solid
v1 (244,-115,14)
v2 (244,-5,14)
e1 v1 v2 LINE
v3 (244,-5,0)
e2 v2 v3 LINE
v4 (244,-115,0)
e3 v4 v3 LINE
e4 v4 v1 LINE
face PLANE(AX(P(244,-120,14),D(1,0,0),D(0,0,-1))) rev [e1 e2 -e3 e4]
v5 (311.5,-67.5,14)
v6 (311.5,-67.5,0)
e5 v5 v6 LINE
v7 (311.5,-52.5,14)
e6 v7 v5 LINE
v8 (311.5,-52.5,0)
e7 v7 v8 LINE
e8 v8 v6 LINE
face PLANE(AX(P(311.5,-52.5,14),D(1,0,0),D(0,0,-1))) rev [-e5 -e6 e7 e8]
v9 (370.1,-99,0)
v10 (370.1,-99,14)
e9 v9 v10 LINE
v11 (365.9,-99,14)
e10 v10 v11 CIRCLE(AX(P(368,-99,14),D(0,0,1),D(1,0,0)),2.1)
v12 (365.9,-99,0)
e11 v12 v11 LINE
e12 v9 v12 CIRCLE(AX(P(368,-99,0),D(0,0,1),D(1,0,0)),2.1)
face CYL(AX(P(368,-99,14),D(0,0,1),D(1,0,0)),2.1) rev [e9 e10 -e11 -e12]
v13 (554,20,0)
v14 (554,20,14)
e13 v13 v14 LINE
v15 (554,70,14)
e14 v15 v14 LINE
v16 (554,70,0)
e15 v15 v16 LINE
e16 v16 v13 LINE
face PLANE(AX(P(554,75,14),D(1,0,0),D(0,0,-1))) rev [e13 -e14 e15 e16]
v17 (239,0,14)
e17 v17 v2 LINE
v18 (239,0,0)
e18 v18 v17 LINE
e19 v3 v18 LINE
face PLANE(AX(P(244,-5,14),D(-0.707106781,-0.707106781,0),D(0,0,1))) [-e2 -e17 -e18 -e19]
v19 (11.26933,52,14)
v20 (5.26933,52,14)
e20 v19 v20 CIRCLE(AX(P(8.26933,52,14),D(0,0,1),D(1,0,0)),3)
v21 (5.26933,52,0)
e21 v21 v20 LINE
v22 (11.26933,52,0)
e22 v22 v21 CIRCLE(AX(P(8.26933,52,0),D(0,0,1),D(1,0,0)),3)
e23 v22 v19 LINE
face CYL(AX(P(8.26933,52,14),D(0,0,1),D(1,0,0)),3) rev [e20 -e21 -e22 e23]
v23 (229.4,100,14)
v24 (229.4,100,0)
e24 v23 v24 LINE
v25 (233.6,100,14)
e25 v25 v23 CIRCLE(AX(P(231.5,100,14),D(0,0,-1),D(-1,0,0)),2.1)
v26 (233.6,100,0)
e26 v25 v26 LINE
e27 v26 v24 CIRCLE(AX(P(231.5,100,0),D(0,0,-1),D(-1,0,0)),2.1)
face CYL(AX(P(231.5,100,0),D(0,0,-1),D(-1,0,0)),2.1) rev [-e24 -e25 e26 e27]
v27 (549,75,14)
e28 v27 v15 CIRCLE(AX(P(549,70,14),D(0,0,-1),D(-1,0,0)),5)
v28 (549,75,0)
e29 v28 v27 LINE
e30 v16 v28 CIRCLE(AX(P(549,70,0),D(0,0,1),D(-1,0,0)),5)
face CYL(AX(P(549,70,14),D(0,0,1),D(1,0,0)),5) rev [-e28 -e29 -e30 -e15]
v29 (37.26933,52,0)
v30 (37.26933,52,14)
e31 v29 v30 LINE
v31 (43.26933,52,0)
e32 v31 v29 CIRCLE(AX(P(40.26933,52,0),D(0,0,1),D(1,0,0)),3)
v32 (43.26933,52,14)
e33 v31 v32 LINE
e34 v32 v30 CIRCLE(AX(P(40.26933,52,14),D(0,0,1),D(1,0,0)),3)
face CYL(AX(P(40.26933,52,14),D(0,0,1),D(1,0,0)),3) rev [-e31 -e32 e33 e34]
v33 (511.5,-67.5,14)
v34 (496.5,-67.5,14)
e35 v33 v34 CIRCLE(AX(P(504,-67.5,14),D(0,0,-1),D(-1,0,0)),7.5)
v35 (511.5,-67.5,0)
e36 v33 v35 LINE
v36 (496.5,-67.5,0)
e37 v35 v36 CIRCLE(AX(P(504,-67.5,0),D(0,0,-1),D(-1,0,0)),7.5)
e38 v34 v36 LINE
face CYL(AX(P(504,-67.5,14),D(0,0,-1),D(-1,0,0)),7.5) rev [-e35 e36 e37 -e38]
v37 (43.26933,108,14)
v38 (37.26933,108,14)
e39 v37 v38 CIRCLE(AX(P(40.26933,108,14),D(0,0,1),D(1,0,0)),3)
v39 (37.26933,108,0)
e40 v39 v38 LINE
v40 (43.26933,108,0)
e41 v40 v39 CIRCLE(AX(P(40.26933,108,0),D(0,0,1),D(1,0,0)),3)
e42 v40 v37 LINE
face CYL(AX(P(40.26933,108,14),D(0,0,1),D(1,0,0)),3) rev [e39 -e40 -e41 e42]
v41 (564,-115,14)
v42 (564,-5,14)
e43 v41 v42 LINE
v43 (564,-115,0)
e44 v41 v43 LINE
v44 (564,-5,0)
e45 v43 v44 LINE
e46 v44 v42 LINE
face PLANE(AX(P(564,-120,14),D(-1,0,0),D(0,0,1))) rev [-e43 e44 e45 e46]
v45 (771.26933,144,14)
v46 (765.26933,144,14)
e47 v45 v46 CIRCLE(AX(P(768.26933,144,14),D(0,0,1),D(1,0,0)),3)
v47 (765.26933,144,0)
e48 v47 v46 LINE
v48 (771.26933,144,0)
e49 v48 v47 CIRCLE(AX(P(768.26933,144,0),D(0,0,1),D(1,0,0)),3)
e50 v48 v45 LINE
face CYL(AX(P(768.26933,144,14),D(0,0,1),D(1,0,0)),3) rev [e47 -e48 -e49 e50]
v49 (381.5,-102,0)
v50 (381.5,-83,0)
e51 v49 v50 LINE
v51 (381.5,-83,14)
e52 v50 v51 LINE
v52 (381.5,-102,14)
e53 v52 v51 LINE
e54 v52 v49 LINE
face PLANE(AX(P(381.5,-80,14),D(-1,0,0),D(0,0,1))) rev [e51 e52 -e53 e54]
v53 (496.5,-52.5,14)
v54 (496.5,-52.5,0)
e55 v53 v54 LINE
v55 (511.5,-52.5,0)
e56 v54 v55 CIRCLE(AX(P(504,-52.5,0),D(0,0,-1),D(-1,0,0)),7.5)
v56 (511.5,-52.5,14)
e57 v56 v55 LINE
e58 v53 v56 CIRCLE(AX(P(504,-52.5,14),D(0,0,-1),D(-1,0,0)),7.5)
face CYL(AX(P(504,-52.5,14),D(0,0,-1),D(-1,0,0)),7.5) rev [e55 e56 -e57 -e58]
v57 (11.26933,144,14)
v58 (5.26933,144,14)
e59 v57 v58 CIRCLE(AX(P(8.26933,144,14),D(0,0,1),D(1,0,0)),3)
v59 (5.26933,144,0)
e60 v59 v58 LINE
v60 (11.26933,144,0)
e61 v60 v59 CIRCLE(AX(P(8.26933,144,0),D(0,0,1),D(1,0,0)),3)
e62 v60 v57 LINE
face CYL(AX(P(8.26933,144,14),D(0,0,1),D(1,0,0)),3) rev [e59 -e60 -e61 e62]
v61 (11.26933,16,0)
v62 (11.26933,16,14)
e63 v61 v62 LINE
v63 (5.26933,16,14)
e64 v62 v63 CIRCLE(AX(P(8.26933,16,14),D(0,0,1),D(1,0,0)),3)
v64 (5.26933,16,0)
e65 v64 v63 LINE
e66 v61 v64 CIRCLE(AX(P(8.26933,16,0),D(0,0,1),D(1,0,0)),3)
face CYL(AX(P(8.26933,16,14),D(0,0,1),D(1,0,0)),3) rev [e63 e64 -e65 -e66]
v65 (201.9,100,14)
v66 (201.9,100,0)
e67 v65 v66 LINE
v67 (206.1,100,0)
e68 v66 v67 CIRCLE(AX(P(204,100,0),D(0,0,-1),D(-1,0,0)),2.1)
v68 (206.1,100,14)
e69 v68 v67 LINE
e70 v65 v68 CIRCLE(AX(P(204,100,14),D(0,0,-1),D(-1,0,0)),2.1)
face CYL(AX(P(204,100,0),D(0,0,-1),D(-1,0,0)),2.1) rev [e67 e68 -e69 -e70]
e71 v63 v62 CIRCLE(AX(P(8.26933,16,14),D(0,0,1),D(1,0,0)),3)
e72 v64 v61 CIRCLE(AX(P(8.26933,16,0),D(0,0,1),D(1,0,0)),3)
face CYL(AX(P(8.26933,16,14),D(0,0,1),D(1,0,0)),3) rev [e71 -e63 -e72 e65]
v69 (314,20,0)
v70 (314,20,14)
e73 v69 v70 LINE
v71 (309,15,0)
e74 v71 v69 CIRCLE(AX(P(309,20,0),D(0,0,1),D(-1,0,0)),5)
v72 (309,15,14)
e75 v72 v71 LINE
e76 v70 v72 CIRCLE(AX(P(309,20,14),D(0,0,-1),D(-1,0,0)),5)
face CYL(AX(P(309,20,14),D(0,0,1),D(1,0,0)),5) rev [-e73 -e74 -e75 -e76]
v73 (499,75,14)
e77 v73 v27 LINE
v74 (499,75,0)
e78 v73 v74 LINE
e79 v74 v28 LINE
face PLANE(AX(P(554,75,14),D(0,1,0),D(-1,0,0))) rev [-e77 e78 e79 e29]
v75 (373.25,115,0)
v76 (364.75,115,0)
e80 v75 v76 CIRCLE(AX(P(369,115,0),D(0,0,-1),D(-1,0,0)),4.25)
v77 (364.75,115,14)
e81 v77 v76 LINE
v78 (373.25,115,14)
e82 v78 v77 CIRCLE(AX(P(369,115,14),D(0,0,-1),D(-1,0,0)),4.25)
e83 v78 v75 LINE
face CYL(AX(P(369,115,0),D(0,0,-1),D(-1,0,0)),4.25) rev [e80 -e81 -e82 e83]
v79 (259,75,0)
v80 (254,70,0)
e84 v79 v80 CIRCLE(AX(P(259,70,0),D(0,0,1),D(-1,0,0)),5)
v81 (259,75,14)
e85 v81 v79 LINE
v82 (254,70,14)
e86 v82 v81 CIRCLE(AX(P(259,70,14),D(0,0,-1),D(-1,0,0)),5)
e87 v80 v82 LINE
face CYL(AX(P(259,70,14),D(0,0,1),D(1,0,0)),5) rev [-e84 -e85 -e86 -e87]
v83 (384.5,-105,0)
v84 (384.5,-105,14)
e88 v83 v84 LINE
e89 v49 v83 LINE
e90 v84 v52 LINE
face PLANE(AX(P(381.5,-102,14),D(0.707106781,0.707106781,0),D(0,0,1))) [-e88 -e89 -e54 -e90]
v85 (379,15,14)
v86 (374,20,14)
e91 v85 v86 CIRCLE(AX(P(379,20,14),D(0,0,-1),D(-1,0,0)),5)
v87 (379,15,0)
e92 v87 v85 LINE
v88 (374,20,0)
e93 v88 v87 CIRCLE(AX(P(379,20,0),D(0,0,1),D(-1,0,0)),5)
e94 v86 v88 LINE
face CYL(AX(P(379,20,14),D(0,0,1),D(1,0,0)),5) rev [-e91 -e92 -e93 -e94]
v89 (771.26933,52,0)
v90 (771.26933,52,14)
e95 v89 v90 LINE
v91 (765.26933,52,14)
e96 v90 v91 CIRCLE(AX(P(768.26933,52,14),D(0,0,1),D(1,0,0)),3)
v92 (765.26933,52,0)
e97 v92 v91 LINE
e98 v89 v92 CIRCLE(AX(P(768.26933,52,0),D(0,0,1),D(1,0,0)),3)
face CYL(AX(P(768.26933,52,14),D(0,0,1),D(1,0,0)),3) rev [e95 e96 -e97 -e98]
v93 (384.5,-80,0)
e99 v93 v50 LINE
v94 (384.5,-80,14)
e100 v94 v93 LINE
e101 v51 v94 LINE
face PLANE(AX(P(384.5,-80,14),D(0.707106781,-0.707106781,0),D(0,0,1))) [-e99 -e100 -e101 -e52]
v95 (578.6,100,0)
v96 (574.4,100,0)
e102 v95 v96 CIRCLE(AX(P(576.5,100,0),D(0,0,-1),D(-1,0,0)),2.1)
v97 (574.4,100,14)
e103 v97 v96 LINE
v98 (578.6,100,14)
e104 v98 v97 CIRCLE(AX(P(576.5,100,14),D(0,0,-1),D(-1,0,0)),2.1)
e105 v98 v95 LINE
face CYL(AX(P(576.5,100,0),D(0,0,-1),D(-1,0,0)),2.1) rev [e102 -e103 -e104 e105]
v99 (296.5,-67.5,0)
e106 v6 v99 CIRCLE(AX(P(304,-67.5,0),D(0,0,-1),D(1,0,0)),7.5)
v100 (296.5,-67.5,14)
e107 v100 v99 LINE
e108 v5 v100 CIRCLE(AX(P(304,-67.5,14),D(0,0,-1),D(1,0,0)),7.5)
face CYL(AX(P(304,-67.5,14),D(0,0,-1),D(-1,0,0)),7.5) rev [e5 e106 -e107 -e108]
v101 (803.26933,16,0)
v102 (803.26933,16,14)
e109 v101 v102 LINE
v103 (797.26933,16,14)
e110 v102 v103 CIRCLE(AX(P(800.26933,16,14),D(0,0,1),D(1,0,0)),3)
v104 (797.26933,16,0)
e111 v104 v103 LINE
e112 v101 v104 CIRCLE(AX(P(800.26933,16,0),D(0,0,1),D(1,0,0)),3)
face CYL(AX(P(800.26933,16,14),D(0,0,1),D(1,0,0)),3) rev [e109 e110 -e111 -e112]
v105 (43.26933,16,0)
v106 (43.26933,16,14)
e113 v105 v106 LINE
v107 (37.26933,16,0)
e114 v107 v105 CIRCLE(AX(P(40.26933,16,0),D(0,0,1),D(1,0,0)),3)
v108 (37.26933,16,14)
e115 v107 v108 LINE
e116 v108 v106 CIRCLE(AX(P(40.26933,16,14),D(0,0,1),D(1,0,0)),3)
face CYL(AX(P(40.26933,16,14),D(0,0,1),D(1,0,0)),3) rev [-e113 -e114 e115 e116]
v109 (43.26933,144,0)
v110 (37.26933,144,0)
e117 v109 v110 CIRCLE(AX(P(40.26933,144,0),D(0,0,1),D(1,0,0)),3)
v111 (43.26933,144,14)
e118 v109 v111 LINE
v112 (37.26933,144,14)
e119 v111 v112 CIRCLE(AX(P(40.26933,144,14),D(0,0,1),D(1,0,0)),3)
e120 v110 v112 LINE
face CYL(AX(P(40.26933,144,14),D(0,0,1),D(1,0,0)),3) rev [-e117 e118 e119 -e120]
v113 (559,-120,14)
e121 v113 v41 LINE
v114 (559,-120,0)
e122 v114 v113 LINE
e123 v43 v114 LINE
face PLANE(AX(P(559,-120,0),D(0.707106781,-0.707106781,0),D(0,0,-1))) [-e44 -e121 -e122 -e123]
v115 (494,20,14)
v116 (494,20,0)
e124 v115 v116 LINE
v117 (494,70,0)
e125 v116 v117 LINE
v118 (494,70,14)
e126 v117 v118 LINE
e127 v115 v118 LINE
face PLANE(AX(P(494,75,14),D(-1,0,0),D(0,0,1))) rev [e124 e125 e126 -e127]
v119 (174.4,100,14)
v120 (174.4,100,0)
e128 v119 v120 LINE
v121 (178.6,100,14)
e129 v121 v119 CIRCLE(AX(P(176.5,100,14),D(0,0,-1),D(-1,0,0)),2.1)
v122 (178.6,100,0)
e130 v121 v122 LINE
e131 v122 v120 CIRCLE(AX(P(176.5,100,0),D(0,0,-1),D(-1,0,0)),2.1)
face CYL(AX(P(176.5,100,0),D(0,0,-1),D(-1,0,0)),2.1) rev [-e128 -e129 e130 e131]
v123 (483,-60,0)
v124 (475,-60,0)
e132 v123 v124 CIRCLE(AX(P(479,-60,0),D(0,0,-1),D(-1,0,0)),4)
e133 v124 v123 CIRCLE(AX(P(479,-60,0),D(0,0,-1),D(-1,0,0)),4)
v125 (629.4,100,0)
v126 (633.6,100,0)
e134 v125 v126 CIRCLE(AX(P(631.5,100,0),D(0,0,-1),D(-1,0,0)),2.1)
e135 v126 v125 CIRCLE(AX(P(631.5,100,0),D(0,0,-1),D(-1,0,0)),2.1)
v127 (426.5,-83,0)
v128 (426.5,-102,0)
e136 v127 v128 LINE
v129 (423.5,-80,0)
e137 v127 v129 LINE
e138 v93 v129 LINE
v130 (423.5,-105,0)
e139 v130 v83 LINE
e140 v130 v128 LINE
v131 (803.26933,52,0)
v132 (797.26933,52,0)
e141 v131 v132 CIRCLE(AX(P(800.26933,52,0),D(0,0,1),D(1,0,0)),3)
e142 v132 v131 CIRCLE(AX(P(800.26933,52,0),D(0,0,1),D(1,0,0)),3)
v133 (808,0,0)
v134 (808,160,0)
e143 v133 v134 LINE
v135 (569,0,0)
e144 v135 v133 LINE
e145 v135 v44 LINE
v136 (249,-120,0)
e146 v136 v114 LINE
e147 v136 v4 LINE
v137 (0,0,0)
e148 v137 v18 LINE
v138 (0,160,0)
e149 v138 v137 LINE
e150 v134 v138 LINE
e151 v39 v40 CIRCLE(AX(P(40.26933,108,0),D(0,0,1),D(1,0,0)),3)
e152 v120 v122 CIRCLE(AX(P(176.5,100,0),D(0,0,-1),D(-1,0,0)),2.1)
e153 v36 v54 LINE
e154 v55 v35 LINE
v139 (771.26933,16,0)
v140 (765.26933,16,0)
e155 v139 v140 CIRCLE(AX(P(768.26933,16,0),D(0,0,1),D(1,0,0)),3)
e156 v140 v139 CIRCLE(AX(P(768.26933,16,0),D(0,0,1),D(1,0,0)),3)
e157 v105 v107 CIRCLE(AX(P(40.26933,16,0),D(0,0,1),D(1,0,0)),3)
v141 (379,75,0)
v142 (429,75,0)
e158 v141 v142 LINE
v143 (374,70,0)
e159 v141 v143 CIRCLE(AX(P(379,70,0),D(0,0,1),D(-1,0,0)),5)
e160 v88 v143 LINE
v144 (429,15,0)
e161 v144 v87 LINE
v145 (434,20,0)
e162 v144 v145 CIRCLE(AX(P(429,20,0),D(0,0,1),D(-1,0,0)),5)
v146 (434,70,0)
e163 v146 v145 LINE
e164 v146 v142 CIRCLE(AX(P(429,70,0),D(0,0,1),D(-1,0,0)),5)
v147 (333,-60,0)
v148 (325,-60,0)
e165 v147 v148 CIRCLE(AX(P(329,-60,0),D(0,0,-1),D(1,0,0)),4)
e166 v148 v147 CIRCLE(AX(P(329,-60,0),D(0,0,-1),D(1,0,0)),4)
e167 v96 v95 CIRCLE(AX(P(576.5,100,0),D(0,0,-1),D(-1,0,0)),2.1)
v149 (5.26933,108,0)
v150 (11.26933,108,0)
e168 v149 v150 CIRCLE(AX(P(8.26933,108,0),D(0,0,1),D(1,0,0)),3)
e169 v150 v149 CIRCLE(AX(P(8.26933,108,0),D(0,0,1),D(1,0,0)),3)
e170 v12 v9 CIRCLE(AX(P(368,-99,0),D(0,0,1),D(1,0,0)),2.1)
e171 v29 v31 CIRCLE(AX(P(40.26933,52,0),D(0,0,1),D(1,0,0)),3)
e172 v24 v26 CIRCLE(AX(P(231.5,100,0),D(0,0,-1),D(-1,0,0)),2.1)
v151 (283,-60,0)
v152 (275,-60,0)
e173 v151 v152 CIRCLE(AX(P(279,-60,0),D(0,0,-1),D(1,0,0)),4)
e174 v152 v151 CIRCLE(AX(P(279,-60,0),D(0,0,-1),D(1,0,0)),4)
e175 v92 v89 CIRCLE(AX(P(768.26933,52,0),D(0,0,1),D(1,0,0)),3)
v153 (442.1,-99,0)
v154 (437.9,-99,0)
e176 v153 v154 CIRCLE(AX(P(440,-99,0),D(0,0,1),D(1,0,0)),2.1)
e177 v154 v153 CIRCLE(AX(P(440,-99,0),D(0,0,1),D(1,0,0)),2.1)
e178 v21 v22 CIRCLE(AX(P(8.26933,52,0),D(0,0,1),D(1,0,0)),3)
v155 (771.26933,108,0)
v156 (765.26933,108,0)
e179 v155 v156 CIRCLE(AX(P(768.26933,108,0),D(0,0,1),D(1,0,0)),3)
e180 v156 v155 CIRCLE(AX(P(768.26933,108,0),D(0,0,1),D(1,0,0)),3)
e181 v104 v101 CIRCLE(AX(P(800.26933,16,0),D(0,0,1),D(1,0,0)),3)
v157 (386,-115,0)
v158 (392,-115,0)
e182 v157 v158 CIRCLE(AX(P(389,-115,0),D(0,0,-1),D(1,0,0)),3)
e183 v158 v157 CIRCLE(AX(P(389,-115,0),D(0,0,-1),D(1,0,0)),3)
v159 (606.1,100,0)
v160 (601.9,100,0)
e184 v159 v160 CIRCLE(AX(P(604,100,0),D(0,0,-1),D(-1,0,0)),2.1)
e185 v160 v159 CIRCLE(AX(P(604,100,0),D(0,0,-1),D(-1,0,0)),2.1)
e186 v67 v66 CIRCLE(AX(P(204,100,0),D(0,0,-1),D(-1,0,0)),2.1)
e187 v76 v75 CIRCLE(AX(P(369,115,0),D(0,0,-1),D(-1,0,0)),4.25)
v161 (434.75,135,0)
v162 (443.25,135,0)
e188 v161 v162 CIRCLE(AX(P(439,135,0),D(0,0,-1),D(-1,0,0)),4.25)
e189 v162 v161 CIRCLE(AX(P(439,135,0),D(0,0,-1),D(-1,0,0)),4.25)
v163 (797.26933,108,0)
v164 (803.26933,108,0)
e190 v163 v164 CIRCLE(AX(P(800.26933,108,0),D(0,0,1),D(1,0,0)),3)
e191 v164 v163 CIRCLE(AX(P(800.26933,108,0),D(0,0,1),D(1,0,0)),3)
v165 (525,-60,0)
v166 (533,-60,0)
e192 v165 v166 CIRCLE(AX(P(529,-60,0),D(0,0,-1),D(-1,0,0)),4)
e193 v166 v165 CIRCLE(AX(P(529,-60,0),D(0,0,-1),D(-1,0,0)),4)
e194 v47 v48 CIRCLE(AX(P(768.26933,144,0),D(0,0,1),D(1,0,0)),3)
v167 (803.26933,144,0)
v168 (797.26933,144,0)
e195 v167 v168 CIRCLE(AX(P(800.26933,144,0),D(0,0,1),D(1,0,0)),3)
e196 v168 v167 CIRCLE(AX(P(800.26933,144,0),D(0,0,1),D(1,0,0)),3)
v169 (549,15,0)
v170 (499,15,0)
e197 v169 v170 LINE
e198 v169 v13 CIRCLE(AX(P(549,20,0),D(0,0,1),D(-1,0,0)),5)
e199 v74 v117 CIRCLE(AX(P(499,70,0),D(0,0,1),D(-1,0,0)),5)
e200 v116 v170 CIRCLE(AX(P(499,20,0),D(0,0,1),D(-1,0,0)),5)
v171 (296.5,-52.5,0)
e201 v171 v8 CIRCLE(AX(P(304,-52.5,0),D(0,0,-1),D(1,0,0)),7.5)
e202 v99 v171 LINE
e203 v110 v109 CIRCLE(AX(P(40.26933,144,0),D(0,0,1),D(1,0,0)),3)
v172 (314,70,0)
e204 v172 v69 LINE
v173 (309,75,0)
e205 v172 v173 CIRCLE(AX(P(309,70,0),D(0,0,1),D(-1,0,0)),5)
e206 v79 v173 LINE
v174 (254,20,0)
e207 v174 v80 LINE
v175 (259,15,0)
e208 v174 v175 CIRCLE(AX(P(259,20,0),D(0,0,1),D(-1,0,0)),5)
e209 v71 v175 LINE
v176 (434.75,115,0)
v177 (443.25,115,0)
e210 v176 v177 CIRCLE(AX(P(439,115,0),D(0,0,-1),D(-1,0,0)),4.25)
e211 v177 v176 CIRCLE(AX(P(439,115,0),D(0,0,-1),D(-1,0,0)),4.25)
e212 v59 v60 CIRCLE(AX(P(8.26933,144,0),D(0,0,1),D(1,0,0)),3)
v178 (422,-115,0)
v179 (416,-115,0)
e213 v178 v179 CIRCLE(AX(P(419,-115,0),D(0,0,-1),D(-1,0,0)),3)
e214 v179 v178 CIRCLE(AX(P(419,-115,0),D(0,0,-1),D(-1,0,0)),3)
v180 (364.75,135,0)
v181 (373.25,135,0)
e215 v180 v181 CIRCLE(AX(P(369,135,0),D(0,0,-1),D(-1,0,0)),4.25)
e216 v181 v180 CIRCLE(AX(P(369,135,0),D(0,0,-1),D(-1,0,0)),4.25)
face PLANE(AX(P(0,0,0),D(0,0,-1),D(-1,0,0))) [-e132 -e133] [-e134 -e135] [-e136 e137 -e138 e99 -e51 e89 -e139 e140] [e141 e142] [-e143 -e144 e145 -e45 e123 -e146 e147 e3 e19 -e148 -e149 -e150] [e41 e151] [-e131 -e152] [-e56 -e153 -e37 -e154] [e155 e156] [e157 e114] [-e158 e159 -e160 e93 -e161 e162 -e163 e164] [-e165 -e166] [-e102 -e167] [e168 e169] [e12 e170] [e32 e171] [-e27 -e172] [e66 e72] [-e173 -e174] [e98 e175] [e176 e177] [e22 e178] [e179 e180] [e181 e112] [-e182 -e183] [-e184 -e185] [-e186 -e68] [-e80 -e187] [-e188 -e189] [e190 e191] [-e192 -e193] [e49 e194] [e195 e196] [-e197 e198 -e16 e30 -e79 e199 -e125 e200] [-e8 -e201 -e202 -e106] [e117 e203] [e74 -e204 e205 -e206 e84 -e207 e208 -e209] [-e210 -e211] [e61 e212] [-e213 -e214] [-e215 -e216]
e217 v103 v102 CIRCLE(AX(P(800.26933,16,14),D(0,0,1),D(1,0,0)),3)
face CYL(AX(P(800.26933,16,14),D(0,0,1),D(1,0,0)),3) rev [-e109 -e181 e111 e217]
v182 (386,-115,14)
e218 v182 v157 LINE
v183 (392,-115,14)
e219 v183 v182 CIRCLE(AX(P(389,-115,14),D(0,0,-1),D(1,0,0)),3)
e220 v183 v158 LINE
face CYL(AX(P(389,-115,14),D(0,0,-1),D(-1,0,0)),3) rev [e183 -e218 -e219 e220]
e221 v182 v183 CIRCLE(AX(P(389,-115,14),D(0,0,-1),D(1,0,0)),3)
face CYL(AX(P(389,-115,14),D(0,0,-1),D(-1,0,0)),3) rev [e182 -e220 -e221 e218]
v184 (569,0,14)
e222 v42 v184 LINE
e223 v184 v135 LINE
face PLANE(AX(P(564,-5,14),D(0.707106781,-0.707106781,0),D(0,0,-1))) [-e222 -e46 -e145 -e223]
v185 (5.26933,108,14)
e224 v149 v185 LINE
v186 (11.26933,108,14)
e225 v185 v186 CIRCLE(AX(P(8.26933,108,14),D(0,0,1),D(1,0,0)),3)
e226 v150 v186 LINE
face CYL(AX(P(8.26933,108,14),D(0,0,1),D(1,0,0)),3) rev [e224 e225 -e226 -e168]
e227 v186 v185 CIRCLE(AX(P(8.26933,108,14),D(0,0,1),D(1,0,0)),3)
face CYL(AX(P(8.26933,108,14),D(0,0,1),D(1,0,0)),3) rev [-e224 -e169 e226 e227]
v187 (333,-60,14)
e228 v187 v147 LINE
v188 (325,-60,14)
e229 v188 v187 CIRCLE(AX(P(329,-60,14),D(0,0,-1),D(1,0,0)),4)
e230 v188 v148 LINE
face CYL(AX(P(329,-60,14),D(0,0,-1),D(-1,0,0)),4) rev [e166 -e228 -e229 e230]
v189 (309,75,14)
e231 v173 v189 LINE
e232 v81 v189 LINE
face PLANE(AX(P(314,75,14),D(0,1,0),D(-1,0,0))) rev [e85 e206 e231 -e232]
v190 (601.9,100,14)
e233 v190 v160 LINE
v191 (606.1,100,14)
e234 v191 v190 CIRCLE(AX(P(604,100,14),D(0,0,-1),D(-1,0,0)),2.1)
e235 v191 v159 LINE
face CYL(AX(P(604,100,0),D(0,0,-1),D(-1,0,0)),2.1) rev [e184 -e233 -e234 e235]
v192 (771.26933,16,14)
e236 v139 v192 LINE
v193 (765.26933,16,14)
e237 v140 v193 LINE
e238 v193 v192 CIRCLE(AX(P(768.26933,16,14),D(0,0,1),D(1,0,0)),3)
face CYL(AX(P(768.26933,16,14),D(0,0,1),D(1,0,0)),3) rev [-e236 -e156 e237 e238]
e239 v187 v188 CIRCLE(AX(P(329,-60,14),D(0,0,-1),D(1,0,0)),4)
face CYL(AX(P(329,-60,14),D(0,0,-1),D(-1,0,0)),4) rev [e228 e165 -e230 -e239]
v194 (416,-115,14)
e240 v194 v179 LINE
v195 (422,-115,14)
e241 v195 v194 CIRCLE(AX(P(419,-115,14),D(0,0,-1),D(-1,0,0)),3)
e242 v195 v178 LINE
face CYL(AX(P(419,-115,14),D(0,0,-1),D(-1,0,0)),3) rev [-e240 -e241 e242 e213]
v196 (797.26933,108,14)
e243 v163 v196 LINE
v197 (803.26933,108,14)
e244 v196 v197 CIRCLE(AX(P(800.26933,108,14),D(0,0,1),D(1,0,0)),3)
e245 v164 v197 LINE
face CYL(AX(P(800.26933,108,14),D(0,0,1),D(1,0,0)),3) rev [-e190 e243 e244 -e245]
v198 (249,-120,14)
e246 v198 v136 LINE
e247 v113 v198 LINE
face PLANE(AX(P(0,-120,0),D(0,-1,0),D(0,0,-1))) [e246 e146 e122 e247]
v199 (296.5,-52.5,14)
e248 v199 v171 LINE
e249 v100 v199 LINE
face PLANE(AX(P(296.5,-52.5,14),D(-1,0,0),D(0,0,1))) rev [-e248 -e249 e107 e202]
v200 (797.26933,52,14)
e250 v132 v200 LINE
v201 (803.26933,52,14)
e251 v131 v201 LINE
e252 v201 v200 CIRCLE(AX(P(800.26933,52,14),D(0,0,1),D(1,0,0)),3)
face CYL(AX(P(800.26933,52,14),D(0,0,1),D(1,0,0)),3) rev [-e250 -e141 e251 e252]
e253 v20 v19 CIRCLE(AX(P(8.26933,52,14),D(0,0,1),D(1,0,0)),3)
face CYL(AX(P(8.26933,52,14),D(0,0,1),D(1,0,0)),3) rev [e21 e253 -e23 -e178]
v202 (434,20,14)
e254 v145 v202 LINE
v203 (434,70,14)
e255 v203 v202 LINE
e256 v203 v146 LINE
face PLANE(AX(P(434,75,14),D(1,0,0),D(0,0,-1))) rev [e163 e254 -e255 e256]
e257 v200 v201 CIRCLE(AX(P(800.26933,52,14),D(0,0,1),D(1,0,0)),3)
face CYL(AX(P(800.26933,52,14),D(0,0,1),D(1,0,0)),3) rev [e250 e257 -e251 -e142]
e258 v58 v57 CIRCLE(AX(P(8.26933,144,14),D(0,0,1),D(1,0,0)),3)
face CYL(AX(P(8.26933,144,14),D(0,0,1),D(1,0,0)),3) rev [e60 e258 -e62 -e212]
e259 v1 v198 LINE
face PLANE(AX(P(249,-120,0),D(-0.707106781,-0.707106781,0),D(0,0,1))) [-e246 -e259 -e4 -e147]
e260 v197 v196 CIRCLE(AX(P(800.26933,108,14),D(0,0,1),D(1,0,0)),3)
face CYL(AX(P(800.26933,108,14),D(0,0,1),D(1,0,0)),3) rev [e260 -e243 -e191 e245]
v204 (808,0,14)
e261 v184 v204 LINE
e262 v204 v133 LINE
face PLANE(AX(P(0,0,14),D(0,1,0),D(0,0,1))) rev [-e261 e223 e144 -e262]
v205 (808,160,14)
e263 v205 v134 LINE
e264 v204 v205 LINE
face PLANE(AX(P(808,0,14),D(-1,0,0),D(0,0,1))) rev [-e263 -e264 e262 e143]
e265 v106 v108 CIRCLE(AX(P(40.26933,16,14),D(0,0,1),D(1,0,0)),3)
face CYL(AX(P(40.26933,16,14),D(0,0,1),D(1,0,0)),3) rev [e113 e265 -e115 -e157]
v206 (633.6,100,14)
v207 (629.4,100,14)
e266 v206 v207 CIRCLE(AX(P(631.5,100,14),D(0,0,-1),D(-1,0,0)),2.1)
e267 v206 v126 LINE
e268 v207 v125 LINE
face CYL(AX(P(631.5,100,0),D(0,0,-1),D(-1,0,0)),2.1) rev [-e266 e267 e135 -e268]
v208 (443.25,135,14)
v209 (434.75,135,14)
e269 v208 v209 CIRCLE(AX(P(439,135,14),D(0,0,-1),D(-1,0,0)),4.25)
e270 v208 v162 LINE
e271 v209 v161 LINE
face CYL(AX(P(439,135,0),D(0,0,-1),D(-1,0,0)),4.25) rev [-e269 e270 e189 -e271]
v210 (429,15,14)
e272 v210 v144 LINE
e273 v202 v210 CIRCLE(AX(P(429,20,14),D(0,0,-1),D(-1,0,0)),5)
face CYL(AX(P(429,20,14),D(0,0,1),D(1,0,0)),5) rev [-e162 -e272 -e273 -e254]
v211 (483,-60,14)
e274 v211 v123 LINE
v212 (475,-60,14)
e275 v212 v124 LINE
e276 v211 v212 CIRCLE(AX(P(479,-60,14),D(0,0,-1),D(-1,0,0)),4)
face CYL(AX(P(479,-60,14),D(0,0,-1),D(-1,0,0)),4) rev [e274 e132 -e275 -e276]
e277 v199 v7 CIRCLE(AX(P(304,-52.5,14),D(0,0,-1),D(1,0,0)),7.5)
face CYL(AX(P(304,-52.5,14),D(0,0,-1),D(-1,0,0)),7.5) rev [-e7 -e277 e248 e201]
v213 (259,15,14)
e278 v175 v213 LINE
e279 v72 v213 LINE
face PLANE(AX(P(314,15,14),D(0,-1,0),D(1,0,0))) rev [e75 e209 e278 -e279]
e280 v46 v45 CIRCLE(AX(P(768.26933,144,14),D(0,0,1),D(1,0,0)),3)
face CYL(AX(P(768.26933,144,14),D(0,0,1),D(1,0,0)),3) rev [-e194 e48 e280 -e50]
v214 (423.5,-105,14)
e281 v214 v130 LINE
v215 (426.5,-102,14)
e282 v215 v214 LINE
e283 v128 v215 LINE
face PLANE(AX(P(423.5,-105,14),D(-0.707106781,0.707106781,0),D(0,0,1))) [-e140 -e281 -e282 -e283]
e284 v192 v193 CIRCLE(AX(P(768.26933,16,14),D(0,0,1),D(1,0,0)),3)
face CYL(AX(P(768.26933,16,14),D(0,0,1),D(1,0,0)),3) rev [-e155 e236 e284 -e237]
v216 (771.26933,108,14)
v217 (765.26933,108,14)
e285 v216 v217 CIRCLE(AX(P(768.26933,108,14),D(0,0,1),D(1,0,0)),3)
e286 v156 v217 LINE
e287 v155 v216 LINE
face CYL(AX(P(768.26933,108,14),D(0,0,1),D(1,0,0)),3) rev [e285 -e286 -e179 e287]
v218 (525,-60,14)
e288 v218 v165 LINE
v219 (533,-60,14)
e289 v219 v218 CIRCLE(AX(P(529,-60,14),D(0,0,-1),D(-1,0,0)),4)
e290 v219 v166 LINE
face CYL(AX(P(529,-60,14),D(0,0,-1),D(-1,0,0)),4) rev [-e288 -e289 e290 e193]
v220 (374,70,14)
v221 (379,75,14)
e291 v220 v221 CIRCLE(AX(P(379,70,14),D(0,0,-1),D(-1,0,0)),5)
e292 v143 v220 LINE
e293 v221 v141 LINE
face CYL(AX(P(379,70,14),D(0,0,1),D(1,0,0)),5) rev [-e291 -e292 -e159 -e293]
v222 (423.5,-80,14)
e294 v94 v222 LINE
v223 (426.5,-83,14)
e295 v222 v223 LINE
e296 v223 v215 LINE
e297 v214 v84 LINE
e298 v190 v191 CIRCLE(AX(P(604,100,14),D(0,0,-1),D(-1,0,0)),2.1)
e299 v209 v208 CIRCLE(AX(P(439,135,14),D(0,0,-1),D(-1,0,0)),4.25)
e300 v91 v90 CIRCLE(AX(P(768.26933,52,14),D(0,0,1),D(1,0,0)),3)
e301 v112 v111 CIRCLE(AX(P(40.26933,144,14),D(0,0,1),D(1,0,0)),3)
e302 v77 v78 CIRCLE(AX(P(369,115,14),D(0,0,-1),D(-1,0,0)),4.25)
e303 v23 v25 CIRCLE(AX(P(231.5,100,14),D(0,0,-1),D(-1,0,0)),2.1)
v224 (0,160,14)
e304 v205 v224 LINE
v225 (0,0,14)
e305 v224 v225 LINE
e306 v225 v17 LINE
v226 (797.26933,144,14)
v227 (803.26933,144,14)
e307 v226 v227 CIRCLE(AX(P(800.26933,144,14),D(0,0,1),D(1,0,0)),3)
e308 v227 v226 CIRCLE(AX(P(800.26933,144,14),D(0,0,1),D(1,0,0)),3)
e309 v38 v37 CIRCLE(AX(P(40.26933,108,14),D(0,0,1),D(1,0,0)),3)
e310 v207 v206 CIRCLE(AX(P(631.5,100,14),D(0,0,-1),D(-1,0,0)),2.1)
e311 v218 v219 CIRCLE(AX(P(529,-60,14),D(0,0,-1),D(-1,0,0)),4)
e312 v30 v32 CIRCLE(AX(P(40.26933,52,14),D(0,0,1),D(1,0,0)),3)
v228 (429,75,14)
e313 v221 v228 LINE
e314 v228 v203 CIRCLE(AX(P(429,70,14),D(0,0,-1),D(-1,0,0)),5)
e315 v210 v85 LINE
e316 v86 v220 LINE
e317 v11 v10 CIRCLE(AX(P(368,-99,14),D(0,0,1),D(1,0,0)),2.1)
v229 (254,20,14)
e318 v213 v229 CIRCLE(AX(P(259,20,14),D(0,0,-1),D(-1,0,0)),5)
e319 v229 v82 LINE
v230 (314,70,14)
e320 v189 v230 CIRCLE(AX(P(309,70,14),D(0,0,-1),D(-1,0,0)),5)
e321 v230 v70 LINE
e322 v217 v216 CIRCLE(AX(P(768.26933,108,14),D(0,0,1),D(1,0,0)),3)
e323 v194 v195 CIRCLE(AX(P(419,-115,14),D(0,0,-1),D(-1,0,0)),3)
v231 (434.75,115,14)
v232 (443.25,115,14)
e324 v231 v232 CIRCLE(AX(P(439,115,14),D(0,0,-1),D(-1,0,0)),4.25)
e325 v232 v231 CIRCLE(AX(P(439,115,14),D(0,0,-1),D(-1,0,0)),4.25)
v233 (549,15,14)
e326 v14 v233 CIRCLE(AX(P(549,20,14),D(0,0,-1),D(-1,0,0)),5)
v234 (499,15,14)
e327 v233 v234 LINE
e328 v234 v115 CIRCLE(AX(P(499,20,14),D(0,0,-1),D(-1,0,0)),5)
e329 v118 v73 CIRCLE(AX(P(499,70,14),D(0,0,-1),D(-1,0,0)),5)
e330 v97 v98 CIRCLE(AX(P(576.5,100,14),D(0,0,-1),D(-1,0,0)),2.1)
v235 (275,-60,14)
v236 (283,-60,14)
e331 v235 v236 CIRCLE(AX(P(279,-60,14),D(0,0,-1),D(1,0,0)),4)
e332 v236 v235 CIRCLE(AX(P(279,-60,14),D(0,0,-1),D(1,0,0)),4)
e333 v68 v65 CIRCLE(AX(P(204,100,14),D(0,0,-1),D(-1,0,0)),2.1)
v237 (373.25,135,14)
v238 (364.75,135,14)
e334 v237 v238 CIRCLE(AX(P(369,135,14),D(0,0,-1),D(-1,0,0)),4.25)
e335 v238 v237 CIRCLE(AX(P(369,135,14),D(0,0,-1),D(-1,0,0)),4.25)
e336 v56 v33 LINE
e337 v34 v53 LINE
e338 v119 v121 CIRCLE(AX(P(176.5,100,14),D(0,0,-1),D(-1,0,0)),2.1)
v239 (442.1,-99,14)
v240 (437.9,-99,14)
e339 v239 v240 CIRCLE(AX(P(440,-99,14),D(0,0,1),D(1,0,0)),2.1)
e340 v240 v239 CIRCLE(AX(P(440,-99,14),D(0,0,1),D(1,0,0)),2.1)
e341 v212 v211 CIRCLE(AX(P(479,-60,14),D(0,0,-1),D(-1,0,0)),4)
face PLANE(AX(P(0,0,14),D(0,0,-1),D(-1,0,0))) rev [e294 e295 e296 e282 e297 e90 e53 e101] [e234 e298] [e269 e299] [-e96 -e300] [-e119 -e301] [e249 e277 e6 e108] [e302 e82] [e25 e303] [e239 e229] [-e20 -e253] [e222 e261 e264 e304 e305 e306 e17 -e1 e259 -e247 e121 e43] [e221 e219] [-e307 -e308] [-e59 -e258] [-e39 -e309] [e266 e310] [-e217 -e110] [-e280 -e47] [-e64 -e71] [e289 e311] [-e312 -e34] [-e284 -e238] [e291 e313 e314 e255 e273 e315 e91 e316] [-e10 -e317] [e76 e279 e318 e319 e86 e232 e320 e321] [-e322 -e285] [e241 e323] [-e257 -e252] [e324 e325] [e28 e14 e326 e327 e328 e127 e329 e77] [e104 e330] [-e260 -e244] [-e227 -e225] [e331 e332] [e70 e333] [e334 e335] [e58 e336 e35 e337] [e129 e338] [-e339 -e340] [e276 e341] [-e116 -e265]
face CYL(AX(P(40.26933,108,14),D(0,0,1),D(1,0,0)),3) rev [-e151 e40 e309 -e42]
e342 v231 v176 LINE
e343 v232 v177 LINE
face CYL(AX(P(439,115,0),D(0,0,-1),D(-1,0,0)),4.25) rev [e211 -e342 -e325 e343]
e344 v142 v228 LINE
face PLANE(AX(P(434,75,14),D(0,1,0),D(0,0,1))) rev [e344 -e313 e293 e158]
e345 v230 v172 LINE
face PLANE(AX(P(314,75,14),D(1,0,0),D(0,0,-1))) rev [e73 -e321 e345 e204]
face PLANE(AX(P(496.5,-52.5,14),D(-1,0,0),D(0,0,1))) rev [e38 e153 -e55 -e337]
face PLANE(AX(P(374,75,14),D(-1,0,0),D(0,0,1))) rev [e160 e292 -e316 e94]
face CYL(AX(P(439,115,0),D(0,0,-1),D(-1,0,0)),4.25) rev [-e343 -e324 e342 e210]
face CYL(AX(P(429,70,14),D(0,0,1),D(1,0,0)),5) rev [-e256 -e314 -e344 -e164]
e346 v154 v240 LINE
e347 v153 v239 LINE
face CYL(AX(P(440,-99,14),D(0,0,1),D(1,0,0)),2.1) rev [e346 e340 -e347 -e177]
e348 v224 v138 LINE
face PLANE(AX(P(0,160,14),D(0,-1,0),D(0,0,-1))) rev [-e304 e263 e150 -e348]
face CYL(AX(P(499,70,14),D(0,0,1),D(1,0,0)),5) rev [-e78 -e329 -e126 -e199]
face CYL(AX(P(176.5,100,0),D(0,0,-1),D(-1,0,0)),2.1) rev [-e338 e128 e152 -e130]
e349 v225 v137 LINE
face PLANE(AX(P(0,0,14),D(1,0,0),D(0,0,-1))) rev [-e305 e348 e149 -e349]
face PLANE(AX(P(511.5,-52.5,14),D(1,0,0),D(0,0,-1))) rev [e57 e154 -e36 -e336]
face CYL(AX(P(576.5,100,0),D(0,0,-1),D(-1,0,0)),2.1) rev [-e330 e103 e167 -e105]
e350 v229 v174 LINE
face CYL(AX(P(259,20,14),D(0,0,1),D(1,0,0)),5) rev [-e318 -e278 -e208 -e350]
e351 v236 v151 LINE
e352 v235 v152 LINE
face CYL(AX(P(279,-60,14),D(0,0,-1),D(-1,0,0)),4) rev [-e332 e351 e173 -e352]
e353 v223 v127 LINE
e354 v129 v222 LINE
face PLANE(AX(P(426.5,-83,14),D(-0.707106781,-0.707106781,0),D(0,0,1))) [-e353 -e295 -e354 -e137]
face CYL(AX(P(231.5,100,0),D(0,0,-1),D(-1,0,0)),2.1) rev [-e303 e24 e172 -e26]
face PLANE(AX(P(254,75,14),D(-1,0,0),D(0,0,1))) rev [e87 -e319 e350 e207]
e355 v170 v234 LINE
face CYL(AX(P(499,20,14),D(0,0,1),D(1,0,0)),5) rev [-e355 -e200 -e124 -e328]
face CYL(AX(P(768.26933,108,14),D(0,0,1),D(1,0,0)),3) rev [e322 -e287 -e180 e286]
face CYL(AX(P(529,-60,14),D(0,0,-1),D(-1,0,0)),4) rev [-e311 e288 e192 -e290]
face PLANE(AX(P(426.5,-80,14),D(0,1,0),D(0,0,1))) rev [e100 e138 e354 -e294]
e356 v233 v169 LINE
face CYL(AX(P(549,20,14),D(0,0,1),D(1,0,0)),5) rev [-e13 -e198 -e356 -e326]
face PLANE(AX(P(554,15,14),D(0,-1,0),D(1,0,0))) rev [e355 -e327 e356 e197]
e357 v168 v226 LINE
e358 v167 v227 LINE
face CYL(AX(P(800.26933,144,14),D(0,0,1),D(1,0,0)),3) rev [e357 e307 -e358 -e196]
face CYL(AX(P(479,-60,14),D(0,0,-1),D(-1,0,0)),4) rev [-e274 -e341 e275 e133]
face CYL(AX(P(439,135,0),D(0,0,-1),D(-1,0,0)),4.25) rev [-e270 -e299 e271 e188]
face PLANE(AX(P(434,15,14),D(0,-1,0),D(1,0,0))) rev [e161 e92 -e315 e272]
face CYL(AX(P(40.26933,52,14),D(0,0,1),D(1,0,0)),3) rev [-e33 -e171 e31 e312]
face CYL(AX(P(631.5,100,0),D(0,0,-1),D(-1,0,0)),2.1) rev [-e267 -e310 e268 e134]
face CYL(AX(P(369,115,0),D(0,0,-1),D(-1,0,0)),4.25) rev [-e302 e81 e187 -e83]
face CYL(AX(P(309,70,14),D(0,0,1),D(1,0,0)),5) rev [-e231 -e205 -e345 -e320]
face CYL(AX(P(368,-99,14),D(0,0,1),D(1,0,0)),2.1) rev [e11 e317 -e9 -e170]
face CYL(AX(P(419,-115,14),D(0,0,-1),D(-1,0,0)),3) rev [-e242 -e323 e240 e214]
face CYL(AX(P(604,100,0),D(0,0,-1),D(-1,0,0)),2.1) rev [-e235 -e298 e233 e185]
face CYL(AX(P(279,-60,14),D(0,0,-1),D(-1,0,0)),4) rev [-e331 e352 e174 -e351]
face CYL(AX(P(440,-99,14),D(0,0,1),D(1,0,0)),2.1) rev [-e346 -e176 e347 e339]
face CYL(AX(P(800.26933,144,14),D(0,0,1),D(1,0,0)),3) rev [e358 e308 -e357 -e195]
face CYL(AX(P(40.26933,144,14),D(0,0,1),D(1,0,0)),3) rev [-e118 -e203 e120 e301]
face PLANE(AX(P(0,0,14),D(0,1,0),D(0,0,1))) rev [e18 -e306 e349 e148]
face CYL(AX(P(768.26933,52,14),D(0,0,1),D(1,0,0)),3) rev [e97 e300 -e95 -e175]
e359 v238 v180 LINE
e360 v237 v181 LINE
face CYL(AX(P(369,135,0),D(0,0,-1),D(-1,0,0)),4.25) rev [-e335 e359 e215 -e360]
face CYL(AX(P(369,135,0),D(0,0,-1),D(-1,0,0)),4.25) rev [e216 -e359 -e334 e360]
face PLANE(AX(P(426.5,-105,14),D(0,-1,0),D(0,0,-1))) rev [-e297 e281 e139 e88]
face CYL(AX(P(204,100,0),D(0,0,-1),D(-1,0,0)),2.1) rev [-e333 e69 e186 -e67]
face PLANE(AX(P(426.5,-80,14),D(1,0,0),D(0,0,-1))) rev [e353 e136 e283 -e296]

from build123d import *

# Parameters (mm, degrees)
SKETCH1_W                = 808
SKETCH1_H                = 160
BOSS_EXTRUDE1_DEPTH      = 14
F_6_0_6_DIAMETER_HOLE1_D = 6
M10_TAPPED_HOLE2_D       = 8.5
LPATTERN3_COUNT          = 2
LPATTERN3_PITCH          = 92
M5_TAPPED_HOLE1_D        = 4.2
M5_TAPPED_HOLE1_DEPTH    = 16.4
M5_TAPPED_HOLE1_TIP      = 1.2618073
SKETCH7_W                = 320
SKETCH7_H                = 14
BOSS_EXTRUDE2_DEPTH      = 120
SKETCH8_R                = 3
SKETCH8_R_2              = 4
SKETCH8_W                = 45
SKETCH8_H                = 25
CUT_EXTRUDE1_DEPTH       = 824.808230112
CHAMFER1_SIZE            = 3
CHAMFER2_SIZE            = 5
SKETCH10_W               = 60
SKETCH10_H               = 60
CUT_EXTRUDE3_DEPTH       = 824.808230112
FILLET1_R                = 5
M5_TAPPED_HOLE2_D        = 4.2


with BuildPart() as part:
    # Sketch1 → Boss-Extrude1 (new body)
    with BuildSketch(Plane.XY):
        with Locations((404, 80)):
            Rectangle(SKETCH1_W, SKETCH1_H)
    extrude(amount=BOSS_EXTRUDE1_DEPTH)

    # Ø6.0 (6) Diameter Hole1 (through all)
    with Locations(Plane(origin=(8.269330411, 52, 14), x_dir=(1, 0, 0), z_dir=(0, 0, 1))):
        with Locations((0, 0), (32, 0), (0, -36), (32, -36), (760, 0), (792, 0), (792, -36), (760, -36)):
            f_6_0_6_diameter_hole1 = Hole(F_6_0_6_DIAMETER_HOLE1_D / 2)

    # M10 Tapped Hole2 (through all)
    with Locations(Plane(origin=(439, 135, 0), x_dir=(-1, 0, 0), z_dir=(0, 0, -1))):
        with Locations((0, 0), (70, 0), (0, -20), (70, -20)):
            Hole(M10_TAPPED_HOLE2_D / 2)

    # LPattern3: Ø6.0 (6) Diameter Hole1 ×2
    with Locations(*[(0, i * LPATTERN3_PITCH, 0) for i in range(1, LPATTERN3_COUNT)]):
        add(f_6_0_6_diameter_hole1, mode=Mode.SUBTRACT)

    # M5 Tapped Hole1
    with Locations(Plane(origin=(0, 0, 0), x_dir=(-1, 0, 0), z_dir=(0, 0, -1))):
        with Locations((-631.5, 100), (-604, 100), (-576.5, 100), (-231.5, 100), (-204, 100), (-176.5, 100)):
            Hole(M5_TAPPED_HOLE1_D / 2, depth=M5_TAPPED_HOLE1_DEPTH)
            with Locations((0, 0, -(M5_TAPPED_HOLE1_DEPTH + M5_TAPPED_HOLE1_TIP / 2))):  # 118° drill point
                Cone(0, M5_TAPPED_HOLE1_D / 2, M5_TAPPED_HOLE1_TIP, mode=Mode.SUBTRACT)

    # Sketch7 → Boss-Extrude2 (add)
    with BuildSketch(Plane.XZ):
        with Locations((404, 7)):
            Rectangle(SKETCH7_W, SKETCH7_H)
    extrude(amount=BOSS_EXTRUDE2_DEPTH)

    # Sketch8 → Cut-Extrude1 (cut, through all)
    with BuildSketch(Plane(origin=(0, 0, 0), x_dir=(-1, 0, 0), z_dir=(0, 0, -1))):
        with Locations((-419, -115)):
            Circle(SKETCH8_R)
        with Locations(Location((-389, -115, 0), (0, 0, 180))):
            Circle(SKETCH8_R)
        with Locations((-529, -60)):
            Circle(SKETCH8_R_2)
        with Locations((-479, -60)):
            Circle(SKETCH8_R_2)
        with Locations(Location((-329, -60, 0), (0, 0, 180))):
            Circle(SKETCH8_R_2)
        with Locations(Location((-279, -60, 0), (0, 0, 180))):
            Circle(SKETCH8_R_2)
        with Locations((-404, -92.5)):
            Rectangle(SKETCH8_W, SKETCH8_H)
        with BuildLine():
            Line((-496.5, -52.5), (-496.5, -67.5))
            ThreePointArc((-496.5, -67.5), (-504, -75), (-511.5, -67.5))
            Line((-511.5, -67.5), (-511.5, -52.5))
            ThreePointArc((-511.5, -52.5), (-504, -45), (-496.5, -52.5))
        make_face()
        with BuildLine():
            Line((-311.5, -52.5), (-311.5, -67.5))
            ThreePointArc((-311.5, -67.5), (-304, -75), (-296.5, -67.5))
            Line((-296.5, -67.5), (-296.5, -52.5))
            ThreePointArc((-296.5, -52.5), (-304, -45), (-311.5, -52.5))
        make_face()
    extrude(amount=-CUT_EXTRUDE1_DEPTH, mode=Mode.SUBTRACT)

    # Chamfer1
    chamfer1_edges = [part.edges().sort_by_distance(p)[0] for p in [
        (426.5, -105, 7),
        (426.5, -80, 7),
        (381.5, -80, 7),
        (381.5, -105, 7),
    ]]
    chamfer(chamfer1_edges, length=CHAMFER1_SIZE)

    # Chamfer2
    chamfer2_edges = [part.edges().sort_by_distance(p)[0] for p in [
        (244, 0, 7),
        (564, 0, 7),
        (244, -120, 7),
        (564, -120, 7),
    ]]
    chamfer(chamfer2_edges, length=CHAMFER2_SIZE)

    # Sketch10 → Cut-Extrude3 (cut, through all)
    with BuildSketch(Plane(origin=(0, 0, 0), x_dir=(-1, 0, 0), z_dir=(0, 0, -1))):
        with Locations((-524, 45)):
            Rectangle(SKETCH10_W, SKETCH10_H)
        with Locations((-404, 45)):
            Rectangle(SKETCH10_W, SKETCH10_H)
        with Locations((-284, 45)):
            Rectangle(SKETCH10_W, SKETCH10_H)
    extrude(amount=-CUT_EXTRUDE3_DEPTH, mode=Mode.SUBTRACT)

    # Fillet1
    fillet1_edges = [part.edges().sort_by_distance(p)[0] for p in [
        (554, 15, 7),
        (554, 75, 7),
        (494, 75, 7),
        (494, 15, 7),
        (434, 15, 7),
        (434, 75, 7),
        (374, 75, 7),
        (374, 15, 7),
        (314, 15, 7),
        (314, 75, 7),
        (254, 75, 7),
        (254, 15, 7),
    ]]
    fillet(fillet1_edges, radius=FILLET1_R)

    # M5 Tapped Hole2 (through all)
    with Locations(Plane.XY.offset(14)):
        with Locations((368, -99), (440, -99)):
            Hole(M5_TAPPED_HOLE2_D / 2)


solid = part.part
